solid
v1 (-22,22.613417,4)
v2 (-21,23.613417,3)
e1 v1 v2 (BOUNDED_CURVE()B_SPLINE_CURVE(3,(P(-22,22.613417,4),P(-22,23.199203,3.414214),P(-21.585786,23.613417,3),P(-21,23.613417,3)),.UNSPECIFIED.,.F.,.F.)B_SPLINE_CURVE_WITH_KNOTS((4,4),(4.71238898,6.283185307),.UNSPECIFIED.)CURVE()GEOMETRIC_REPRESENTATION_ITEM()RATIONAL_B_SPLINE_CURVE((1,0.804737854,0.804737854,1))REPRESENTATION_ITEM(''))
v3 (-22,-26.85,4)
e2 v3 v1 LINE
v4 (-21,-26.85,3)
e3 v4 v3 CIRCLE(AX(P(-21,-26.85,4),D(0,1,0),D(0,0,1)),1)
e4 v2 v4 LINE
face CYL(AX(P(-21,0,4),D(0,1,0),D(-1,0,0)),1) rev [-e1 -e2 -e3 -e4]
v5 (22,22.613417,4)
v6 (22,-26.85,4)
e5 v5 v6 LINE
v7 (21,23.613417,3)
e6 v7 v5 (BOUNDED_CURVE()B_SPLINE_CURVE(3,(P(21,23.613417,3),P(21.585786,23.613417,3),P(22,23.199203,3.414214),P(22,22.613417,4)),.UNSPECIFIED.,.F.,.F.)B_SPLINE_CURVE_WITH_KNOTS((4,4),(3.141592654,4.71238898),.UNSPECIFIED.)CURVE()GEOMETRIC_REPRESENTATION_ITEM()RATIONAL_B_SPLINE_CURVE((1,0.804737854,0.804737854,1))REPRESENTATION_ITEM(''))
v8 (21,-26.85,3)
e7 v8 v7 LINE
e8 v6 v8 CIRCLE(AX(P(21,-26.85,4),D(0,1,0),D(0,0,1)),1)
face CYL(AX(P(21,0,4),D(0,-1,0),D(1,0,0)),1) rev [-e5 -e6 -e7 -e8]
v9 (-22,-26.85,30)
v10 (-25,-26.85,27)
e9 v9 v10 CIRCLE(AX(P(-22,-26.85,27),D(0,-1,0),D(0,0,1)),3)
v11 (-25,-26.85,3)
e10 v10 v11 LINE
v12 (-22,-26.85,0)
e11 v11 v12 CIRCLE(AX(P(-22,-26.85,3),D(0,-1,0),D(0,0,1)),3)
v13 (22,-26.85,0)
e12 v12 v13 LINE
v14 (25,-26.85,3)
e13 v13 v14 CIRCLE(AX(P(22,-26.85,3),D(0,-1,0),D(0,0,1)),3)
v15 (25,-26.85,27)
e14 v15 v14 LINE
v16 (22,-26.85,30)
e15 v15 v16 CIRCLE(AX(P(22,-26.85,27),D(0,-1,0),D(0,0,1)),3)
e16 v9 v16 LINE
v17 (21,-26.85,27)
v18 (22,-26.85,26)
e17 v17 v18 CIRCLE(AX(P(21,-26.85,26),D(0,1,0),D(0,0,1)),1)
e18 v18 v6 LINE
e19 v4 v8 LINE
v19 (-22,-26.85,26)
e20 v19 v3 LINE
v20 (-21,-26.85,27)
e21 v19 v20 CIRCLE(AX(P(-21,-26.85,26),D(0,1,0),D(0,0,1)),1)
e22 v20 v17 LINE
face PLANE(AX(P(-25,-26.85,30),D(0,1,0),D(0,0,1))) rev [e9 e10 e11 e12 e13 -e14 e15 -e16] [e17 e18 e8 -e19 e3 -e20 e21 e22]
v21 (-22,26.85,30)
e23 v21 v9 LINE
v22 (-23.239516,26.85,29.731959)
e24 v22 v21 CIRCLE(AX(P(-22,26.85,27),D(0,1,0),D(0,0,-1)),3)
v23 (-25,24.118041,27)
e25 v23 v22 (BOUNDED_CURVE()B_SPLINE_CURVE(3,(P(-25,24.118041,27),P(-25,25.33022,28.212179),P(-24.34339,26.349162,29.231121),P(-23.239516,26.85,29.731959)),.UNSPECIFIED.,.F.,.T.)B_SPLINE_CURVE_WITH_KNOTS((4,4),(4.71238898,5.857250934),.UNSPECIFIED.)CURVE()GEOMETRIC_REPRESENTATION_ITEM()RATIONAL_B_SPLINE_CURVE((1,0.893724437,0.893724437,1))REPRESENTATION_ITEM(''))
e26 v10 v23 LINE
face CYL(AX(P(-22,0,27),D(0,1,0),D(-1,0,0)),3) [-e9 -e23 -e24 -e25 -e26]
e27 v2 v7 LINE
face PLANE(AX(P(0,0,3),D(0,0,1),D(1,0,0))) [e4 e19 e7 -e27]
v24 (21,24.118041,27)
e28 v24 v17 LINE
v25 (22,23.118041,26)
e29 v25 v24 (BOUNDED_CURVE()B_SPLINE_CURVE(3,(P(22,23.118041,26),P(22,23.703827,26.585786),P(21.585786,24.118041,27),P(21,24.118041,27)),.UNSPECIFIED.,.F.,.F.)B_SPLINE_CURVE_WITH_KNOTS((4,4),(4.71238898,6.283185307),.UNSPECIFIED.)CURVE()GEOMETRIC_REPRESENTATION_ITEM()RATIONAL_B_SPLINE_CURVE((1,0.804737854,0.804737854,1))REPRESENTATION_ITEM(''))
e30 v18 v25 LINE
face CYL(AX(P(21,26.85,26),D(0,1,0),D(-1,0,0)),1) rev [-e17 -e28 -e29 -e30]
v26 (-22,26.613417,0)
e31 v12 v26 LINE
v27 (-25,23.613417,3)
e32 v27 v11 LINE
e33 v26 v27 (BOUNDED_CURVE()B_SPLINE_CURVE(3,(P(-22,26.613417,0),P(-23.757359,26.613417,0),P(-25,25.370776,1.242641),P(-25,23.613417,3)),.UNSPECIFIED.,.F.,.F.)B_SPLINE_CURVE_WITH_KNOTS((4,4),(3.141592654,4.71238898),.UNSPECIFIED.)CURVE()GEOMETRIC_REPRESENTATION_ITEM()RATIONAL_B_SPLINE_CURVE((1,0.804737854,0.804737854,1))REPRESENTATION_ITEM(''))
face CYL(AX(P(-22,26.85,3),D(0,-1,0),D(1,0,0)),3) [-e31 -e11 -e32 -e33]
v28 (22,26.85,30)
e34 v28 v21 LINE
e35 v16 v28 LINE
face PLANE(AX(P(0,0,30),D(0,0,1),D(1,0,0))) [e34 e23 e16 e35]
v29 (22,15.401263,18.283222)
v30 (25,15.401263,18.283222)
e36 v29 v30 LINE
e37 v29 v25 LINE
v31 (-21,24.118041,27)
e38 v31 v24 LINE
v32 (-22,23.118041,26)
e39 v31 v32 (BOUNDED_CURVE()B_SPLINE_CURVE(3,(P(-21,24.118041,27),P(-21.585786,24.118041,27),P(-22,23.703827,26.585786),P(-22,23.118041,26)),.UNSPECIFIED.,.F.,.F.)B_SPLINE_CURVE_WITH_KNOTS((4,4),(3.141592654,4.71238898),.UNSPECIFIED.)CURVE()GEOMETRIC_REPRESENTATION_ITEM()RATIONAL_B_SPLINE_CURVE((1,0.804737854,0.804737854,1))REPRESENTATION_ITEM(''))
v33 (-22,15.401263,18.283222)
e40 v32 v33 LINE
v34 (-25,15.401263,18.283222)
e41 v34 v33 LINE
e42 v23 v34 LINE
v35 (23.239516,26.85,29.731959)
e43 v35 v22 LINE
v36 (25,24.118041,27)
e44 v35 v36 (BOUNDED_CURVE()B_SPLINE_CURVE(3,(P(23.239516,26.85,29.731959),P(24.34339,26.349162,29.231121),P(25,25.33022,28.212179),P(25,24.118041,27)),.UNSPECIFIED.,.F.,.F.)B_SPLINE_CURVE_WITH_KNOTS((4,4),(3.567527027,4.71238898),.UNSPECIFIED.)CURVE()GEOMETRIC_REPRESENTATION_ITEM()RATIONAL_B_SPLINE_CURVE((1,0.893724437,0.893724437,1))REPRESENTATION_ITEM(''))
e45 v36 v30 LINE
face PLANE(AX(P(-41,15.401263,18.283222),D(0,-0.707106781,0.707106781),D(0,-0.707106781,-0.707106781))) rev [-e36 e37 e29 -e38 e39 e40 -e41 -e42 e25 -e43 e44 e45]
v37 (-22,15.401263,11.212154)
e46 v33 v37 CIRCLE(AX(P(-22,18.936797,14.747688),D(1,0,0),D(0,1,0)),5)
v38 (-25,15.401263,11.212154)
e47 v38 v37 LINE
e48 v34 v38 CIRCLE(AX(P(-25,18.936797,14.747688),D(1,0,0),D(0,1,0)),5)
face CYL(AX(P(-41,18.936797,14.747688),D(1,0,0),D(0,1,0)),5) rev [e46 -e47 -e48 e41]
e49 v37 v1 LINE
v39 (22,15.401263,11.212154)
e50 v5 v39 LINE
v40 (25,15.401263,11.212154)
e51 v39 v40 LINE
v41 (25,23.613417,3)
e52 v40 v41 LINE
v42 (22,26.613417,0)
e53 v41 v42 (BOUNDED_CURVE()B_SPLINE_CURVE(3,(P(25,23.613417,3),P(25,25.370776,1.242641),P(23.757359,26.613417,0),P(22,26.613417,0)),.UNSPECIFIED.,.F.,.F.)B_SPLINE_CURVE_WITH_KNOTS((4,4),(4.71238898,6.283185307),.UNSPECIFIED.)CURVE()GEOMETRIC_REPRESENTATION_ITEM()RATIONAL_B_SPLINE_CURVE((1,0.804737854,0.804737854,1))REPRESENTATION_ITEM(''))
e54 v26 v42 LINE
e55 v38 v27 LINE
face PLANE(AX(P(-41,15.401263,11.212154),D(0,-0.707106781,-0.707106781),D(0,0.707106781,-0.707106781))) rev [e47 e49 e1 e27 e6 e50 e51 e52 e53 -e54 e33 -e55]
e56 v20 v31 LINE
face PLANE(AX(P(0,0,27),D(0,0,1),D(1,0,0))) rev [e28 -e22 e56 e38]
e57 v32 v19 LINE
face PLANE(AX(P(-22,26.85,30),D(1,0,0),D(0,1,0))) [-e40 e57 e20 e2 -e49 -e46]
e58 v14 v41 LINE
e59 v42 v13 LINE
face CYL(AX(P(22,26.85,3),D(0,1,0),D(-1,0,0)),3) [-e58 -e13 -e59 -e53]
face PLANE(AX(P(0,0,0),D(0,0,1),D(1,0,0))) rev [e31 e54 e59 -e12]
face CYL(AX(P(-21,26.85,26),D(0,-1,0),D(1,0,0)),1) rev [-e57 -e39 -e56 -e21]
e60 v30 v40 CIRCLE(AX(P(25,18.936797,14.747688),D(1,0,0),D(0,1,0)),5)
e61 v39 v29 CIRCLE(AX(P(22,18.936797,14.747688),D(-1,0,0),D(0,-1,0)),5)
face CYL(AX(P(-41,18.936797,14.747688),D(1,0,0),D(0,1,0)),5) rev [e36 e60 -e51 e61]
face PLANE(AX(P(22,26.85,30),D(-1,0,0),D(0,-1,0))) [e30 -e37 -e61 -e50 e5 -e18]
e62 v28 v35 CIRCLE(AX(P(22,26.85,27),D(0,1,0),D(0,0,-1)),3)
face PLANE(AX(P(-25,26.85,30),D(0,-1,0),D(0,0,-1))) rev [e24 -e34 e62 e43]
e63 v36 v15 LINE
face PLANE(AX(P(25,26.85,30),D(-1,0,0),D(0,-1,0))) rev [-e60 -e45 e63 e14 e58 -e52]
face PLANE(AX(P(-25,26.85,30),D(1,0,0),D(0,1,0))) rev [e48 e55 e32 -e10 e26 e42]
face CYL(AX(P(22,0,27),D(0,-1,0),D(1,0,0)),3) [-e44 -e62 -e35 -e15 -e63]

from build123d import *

# Parameters (mm, degrees)
SKETCH1_W           = 50
SKETCH1_H           = 53.7
BOSS_EXTRUDE1_DEPTH = 30
SHELL1_T            = -3
CUT_EXTRUDE1_DEPTH  = 66
FILLET1_R           = 3
FILLET2_R           = 1


with BuildPart() as part:
    # Sketch1 → Boss-Extrude1 (new body)
    with BuildSketch(Plane.XY):
        Rectangle(SKETCH1_W, SKETCH1_H)
    extrude(amount=BOSS_EXTRUDE1_DEPTH)

    # Shell1
    shell1_openings = [part.faces().sort_by_distance(p)[0] for p in [
        (0, -26.85, 15),
        (0, 26.85, 15),
    ]]
    offset(amount=SHELL1_T, openings=shell1_openings, kind=Kind.INTERSECTION)

    # Sketch2 → Cut-Extrude1 (cut)
    with BuildSketch(Plane(origin=(25, 0, 0), x_dir=(0, 0, -1), z_dir=(1, 0, 0))):
        with BuildLine():
            Line((-11.212154068, 15.401262658), (13.536583273, 40.15))
            Line((13.536583273, 40.15), (-14.747687974, 68.434271247))
            Line((-14.747687974, 68.434271247), (-43.031959221, 40.15))
            Line((-43.031959221, 40.15), (-18.28322188, 15.401262658))
            ThreePointArc((-18.28322188, 15.401262658), (-14.747687974, 13.936796564), (-11.212154068, 15.401262658))
        make_face()
    extrude(amount=-CUT_EXTRUDE1_DEPTH, mode=Mode.SUBTRACT)

    # Fillet1
    fillet1_edges = [part.edges().sort_by_distance(p)[0] for p in [
        (-25, -0.118291637, 0),
        (25, -0.118291637, 0),
        (-25, 0, 30),
        (25, 0, 30),
    ]]
    fillet(fillet1_edges, radius=FILLET1_R)

    # Fillet2
    fillet2_edges = [part.edges().sort_by_distance(p)[0] for p in [
        (22, -1.618291637, 3),
        (22, -1.365979611, 27),
        (-22, -1.618291637, 3),
        (-22, -1.365979611, 27),
    ]]
    fillet(fillet2_edges, radius=FILLET2_R)


solid = part.part
